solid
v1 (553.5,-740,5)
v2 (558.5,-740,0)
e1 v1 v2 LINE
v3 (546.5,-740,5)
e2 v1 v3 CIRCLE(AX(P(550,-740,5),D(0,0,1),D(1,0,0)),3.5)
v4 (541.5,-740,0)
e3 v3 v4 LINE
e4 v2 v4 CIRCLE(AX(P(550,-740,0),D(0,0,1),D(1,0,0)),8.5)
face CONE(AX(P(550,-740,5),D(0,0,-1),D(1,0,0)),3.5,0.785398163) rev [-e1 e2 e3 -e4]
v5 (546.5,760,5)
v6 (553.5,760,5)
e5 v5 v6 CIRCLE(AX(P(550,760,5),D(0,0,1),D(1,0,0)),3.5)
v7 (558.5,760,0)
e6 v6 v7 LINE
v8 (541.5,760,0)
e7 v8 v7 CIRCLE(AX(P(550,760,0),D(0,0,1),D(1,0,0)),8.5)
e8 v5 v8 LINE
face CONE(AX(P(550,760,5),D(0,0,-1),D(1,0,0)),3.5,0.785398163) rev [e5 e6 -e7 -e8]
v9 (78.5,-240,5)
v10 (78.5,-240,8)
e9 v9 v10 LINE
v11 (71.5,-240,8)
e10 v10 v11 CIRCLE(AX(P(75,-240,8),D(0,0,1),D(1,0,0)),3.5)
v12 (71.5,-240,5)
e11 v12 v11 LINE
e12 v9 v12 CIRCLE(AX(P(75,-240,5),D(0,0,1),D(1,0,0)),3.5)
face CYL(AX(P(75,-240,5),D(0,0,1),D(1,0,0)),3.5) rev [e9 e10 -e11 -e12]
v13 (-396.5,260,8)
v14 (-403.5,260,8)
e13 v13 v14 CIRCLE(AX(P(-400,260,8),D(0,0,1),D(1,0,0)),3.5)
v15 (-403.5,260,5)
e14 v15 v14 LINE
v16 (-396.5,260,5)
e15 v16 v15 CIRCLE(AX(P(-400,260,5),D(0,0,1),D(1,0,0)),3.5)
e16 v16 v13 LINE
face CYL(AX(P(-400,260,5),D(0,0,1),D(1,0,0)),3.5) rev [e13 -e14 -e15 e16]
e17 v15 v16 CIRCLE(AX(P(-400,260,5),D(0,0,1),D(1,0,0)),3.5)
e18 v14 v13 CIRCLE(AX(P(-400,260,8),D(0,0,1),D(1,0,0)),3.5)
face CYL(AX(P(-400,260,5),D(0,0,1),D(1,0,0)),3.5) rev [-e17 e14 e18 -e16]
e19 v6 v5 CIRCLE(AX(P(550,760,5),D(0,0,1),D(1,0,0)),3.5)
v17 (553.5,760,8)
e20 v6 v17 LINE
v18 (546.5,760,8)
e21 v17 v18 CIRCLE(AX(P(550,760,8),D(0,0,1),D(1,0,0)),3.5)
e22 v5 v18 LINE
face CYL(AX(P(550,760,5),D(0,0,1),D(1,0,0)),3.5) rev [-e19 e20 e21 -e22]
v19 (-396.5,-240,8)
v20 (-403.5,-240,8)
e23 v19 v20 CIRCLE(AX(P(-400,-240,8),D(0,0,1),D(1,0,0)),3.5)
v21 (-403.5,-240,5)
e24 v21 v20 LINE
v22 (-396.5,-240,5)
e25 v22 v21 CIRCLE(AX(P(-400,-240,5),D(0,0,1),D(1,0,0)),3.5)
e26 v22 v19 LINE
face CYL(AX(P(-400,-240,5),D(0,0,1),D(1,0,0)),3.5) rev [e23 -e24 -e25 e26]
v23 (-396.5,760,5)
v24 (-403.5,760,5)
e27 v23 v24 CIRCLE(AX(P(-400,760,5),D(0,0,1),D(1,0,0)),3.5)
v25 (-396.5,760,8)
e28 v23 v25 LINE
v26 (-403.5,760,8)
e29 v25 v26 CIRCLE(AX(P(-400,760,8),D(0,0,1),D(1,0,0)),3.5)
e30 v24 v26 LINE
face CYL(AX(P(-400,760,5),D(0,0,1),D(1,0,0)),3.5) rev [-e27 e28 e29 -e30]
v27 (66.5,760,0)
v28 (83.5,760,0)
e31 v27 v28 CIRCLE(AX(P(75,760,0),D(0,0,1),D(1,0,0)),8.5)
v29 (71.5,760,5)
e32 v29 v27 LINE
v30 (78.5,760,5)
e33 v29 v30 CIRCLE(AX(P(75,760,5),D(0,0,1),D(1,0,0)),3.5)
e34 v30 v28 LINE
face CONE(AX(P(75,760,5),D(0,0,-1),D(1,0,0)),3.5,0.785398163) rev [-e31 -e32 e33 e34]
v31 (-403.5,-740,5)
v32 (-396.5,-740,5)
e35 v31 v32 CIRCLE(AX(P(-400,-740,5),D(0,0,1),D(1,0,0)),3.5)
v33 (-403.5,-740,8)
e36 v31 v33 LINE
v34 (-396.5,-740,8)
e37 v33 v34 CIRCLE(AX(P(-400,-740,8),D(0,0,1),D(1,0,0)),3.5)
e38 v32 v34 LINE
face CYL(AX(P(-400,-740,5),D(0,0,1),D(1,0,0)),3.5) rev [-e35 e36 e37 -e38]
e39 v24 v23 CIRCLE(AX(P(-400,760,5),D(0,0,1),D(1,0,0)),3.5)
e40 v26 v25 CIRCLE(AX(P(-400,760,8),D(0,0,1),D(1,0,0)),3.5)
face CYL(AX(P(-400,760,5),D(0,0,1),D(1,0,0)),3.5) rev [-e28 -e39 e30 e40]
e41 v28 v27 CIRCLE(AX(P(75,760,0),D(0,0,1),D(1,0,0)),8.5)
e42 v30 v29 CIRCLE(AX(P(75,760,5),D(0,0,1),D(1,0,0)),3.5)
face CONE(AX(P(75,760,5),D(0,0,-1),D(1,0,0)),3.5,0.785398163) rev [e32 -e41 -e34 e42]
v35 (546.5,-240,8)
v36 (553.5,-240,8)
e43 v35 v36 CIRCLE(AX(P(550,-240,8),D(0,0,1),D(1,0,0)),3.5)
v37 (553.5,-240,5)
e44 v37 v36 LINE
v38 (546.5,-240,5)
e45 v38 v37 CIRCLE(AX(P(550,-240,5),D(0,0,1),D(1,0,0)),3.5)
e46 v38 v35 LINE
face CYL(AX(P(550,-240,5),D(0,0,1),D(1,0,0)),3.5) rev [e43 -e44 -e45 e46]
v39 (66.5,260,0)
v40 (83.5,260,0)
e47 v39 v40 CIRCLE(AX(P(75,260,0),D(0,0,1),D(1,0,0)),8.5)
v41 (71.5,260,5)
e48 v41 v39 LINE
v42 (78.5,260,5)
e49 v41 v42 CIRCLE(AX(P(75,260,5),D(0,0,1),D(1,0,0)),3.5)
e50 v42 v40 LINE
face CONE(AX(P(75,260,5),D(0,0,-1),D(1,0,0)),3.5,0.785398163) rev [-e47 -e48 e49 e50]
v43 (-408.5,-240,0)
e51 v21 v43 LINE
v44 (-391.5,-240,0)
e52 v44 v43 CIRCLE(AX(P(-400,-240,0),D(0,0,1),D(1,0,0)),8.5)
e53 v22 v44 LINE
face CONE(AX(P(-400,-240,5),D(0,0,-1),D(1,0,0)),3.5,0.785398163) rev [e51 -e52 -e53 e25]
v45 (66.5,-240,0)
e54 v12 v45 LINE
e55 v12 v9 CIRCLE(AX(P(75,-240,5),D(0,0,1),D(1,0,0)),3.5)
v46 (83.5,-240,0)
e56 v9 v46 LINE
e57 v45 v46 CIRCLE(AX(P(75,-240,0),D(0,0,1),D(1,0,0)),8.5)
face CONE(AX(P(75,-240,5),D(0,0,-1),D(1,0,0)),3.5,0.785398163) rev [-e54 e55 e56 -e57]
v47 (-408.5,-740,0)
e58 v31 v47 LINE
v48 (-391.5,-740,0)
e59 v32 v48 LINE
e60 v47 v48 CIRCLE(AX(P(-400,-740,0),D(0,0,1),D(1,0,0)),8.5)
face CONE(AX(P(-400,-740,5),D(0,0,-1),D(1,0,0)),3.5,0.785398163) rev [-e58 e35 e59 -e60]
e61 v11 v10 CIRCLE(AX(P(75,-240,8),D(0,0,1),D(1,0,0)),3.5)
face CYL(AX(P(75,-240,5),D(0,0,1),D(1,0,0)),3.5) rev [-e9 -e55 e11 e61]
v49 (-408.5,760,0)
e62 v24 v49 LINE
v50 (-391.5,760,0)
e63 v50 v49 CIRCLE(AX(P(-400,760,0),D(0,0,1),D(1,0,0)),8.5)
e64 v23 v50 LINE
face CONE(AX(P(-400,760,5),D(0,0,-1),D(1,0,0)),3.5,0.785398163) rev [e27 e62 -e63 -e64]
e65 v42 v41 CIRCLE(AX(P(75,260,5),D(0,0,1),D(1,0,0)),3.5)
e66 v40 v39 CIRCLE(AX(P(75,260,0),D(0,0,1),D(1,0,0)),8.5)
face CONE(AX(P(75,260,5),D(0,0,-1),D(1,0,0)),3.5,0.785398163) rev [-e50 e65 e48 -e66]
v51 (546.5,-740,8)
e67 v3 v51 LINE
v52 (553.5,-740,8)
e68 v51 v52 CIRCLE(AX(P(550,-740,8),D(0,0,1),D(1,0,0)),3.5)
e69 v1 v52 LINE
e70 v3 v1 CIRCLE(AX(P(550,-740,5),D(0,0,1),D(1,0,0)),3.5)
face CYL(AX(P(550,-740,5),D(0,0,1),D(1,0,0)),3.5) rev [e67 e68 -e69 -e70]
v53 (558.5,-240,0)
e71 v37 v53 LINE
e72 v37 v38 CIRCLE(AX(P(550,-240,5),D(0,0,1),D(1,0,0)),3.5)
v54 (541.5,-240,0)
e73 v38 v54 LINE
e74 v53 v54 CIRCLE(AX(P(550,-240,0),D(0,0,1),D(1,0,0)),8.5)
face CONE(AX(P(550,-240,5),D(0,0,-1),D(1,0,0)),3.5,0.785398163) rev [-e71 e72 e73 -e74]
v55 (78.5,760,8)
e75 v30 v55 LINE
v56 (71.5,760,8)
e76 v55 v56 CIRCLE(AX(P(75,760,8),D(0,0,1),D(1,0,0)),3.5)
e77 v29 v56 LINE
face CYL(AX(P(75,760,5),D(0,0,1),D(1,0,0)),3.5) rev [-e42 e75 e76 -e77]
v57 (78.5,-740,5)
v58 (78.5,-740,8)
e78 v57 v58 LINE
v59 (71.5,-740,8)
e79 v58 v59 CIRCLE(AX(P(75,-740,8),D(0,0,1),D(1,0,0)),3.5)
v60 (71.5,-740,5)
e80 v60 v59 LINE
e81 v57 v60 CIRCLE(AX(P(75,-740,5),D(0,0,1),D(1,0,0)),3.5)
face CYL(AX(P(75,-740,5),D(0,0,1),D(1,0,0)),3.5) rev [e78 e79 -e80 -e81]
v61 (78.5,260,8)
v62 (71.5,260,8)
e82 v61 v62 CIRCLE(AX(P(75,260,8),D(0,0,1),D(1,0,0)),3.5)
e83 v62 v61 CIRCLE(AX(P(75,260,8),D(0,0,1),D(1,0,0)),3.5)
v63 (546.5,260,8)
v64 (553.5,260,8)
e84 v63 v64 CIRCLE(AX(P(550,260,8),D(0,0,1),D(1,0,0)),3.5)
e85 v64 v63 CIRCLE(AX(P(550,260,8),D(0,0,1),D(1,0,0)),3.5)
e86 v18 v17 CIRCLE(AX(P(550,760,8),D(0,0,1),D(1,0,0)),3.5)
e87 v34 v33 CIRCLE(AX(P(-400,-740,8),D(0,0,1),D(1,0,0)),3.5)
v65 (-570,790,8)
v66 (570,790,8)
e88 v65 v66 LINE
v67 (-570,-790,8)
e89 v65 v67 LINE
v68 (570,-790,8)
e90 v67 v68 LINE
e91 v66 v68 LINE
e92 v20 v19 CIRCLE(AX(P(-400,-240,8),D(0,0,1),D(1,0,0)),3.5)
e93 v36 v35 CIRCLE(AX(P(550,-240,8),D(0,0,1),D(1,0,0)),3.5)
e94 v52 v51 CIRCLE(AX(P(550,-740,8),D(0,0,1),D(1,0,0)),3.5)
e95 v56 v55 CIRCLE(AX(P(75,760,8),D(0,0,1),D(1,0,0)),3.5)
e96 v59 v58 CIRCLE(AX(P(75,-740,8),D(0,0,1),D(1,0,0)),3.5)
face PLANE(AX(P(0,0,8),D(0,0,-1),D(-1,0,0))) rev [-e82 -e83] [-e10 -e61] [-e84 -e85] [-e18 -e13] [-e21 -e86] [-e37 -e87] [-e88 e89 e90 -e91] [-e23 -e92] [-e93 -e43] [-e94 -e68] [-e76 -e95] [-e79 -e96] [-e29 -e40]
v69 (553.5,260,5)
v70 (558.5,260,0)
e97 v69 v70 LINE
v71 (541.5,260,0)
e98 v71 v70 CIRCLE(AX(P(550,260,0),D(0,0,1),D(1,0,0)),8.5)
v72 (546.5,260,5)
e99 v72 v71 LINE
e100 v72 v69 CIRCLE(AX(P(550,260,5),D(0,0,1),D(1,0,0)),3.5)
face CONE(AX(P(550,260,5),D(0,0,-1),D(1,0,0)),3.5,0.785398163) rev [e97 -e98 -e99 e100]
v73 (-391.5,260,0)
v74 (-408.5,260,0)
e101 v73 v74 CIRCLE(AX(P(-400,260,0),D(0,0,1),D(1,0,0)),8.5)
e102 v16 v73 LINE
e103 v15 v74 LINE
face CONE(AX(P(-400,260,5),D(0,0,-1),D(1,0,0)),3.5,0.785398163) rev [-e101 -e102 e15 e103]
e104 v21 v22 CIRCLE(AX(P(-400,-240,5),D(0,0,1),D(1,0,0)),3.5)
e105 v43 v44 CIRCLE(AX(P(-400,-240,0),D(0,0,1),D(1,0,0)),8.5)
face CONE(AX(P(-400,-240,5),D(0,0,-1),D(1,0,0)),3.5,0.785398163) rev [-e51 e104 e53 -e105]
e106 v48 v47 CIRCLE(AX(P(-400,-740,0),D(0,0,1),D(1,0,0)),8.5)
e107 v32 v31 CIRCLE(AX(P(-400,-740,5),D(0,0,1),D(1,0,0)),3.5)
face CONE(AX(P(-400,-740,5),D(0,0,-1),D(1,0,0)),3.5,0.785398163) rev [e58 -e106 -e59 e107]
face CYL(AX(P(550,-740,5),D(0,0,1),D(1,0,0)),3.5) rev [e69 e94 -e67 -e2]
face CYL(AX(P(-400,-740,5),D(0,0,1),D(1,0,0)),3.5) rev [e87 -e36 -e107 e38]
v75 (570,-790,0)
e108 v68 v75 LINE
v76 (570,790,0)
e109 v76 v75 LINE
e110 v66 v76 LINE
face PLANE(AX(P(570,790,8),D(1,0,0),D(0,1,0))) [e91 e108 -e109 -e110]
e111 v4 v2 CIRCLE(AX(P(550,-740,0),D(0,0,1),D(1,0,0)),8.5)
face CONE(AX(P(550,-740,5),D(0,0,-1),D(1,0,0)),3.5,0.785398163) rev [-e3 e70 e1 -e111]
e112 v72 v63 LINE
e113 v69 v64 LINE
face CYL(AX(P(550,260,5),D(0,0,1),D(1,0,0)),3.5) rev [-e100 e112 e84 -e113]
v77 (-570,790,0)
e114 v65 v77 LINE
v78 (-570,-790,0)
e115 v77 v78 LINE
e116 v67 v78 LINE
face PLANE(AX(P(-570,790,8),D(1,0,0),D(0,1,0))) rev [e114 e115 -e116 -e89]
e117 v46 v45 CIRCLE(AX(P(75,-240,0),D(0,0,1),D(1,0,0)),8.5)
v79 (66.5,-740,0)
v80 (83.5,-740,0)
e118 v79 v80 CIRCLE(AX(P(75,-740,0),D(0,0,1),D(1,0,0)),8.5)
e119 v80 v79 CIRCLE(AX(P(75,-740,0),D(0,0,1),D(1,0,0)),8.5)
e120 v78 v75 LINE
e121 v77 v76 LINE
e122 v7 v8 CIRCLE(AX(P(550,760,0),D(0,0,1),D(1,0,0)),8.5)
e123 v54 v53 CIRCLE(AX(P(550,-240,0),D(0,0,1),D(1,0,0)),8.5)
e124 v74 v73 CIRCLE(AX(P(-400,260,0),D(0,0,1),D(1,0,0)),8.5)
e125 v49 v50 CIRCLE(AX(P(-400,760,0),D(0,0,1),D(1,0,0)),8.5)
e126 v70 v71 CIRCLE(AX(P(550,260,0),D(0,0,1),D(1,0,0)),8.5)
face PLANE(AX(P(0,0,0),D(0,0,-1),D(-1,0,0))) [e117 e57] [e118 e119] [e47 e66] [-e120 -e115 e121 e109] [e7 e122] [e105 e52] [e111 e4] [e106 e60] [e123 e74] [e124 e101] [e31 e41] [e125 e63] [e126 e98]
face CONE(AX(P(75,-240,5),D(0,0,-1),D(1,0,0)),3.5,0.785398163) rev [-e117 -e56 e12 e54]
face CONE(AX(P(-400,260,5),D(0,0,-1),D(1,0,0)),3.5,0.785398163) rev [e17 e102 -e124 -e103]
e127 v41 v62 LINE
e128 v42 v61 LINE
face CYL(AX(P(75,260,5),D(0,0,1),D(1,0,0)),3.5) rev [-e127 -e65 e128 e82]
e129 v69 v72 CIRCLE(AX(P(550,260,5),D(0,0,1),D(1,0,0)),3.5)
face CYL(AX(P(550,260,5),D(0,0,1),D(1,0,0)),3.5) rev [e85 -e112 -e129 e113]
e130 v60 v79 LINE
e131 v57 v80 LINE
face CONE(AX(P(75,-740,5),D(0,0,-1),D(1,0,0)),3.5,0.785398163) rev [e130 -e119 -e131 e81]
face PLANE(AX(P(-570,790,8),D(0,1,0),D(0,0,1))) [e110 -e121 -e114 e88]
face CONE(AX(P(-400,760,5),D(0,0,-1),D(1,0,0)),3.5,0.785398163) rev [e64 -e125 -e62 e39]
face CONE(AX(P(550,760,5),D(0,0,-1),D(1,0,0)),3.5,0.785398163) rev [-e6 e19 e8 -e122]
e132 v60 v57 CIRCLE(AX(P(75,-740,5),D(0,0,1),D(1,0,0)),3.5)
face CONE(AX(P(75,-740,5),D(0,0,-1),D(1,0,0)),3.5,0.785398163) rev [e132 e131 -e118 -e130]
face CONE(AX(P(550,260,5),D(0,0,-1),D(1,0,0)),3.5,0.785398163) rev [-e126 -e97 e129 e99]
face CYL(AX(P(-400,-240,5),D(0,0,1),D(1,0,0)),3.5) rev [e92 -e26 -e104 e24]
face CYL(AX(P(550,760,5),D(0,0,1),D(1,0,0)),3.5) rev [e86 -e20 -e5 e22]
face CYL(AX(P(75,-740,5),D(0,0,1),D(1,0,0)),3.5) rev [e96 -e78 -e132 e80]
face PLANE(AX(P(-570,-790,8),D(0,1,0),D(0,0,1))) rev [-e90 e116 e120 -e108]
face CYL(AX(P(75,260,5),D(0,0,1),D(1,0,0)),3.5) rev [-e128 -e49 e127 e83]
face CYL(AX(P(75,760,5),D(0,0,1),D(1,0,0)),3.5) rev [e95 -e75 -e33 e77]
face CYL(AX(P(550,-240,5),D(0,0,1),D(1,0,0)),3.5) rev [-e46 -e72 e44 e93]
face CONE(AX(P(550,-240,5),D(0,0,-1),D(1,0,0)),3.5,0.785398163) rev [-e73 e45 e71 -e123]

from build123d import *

# Parameters (mm, degrees)
SKETCH1_W                     = 1140
SKETCH1_H                     = 1580
BOSS_EXTRUDE1_DEPTH           = 8
SKETCH2_R                     = 3.5
CUT_EXTRUDE1_DEPTH            = 3
SKETCH3_R                     = 3.5
CUT_EXTRUDE2_DEPTH            = 5
CUT_EXTRUDE2_DRAFT            = 45
CUT_EXTRUDE2_PROFILE_2_DEPTH  = 5
CUT_EXTRUDE2_PROFILE_2_DRAFT  = 45
CUT_EXTRUDE2_PROFILE_3_DEPTH  = 5
CUT_EXTRUDE2_PROFILE_3_DRAFT  = 45
CUT_EXTRUDE2_PROFILE_4_DEPTH  = 5
CUT_EXTRUDE2_PROFILE_4_DRAFT  = 45
CUT_EXTRUDE2_PROFILE_5_DEPTH  = 5
CUT_EXTRUDE2_PROFILE_5_DRAFT  = 45
CUT_EXTRUDE2_PROFILE_6_DEPTH  = 5
CUT_EXTRUDE2_PROFILE_6_DRAFT  = 45
CUT_EXTRUDE2_PROFILE_7_DEPTH  = 5
CUT_EXTRUDE2_PROFILE_7_DRAFT  = 45
CUT_EXTRUDE2_PROFILE_8_DEPTH  = 5
CUT_EXTRUDE2_PROFILE_8_DRAFT  = 45
CUT_EXTRUDE2_PROFILE_9_DEPTH  = 5
CUT_EXTRUDE2_PROFILE_9_DRAFT  = 45
CUT_EXTRUDE2_PROFILE_10_DEPTH = 5
CUT_EXTRUDE2_PROFILE_10_DRAFT = 45
CUT_EXTRUDE2_PROFILE_11_DEPTH = 5
CUT_EXTRUDE2_PROFILE_11_DRAFT = 45
CUT_EXTRUDE2_PROFILE_12_DEPTH = 5
CUT_EXTRUDE2_PROFILE_12_DRAFT = 45


with BuildPart() as part:
    # Sketch1 → Boss-Extrude1 (new body)
    with BuildSketch(Plane.XY):
        Rectangle(SKETCH1_W, SKETCH1_H)
    extrude(amount=BOSS_EXTRUDE1_DEPTH)

    # Sketch2 → Cut-Extrude1 (cut)
    with BuildSketch(Plane.XY.offset(8)):
        with Locations((-400, -240)):
            Circle(SKETCH2_R)
        with Locations((75, -240)):
            Circle(SKETCH2_R)
        with Locations((550, -240)):
            Circle(SKETCH2_R)
        with Locations((-400, 260)):
            Circle(SKETCH2_R)
        with Locations((75, 260)):
            Circle(SKETCH2_R)
        with Locations((550, 260)):
            Circle(SKETCH2_R)
        with Locations((-400, 760)):
            Circle(SKETCH2_R)
        with Locations((75, 760)):
            Circle(SKETCH2_R)
        with Locations((550, 760)):
            Circle(SKETCH2_R)
        with Locations((-400, -740)):
            Circle(SKETCH2_R)
        with Locations((75, -740)):
            Circle(SKETCH2_R)
        with Locations((550, -740)):
            Circle(SKETCH2_R)
    extrude(amount=-CUT_EXTRUDE1_DEPTH, mode=Mode.SUBTRACT)


with BuildPart() as cut_extrude2_tool:
    # Sketch3 → Cut-Extrude2 (with draft: the straight prism first)
    with BuildSketch(Plane.XY.offset(5)):
        with Locations((550, -740)):
            Circle(SKETCH3_R)
    extrude(amount=-CUT_EXTRUDE2_DEPTH)
    # Cut-Extrude2: the draft: its side faces are tilted about the plane it starts from
    cut_extrude2_sides = [cut_extrude2_tool.faces().sort_by_distance(p)[0] for p in [
        (546.5, -740, 2.5),
    ]]
    draft(cut_extrude2_sides, Plane.XY.offset(5), CUT_EXTRUDE2_DRAFT)


with BuildPart() as part_1:
    add(part.part)

    # Cut-Extrude2: cut by cut_extrude2_tool
    add(cut_extrude2_tool.part, mode=Mode.SUBTRACT)


with BuildPart() as cut_extrude2_profile_2_tool:
    # Sketch3 → Cut-Extrude2 profile 2 (with draft: the straight prism first)
    with BuildSketch(Plane.XY.offset(5)):
        with Locations((75, -740)):
            Circle(SKETCH3_R)
    extrude(amount=-CUT_EXTRUDE2_PROFILE_2_DEPTH)
    # Cut-Extrude2 profile 2: the draft: its side faces are tilted about the plane it starts from
    cut_extrude2_profile_2_sides = [cut_extrude2_profile_2_tool.faces().sort_by_distance(p)[0] for p in [
        (71.5, -740, 2.5),
    ]]
    draft(cut_extrude2_profile_2_sides, Plane.XY.offset(5), CUT_EXTRUDE2_PROFILE_2_DRAFT)


with BuildPart() as part_2:
    add(part_1.part)

    # Cut-Extrude2 profile 2: cut by cut_extrude2_profile_2_tool
    add(cut_extrude2_profile_2_tool.part, mode=Mode.SUBTRACT)


with BuildPart() as cut_extrude2_profile_3_tool:
    # Sketch3 → Cut-Extrude2 profile 3 (with draft: the straight prism first)
    with BuildSketch(Plane.XY.offset(5)):
        with Locations((-400, -740)):
            Circle(SKETCH3_R)
    extrude(amount=-CUT_EXTRUDE2_PROFILE_3_DEPTH)
    # Cut-Extrude2 profile 3: the draft: its side faces are tilted about the plane it starts from
    cut_extrude2_profile_3_sides = [cut_extrude2_profile_3_tool.faces().sort_by_distance(p)[0] for p in [
        (-403.5, -740, 2.5),
    ]]
    draft(cut_extrude2_profile_3_sides, Plane.XY.offset(5), CUT_EXTRUDE2_PROFILE_3_DRAFT)


with BuildPart() as part_3:
    add(part_2.part)

    # Cut-Extrude2 profile 3: cut by cut_extrude2_profile_3_tool
    add(cut_extrude2_profile_3_tool.part, mode=Mode.SUBTRACT)


with BuildPart() as cut_extrude2_profile_4_tool:
    # Sketch3 → Cut-Extrude2 profile 4 (with draft: the straight prism first)
    with BuildSketch(Plane.XY.offset(5)):
        with Locations((-400, -240)):
            Circle(SKETCH3_R)
    extrude(amount=-CUT_EXTRUDE2_PROFILE_4_DEPTH)
    # Cut-Extrude2 profile 4: the draft: its side faces are tilted about the plane it starts from
    cut_extrude2_profile_4_sides = [cut_extrude2_profile_4_tool.faces().sort_by_distance(p)[0] for p in [
        (-403.5, -240, 2.5),
    ]]
    draft(cut_extrude2_profile_4_sides, Plane.XY.offset(5), CUT_EXTRUDE2_PROFILE_4_DRAFT)


with BuildPart() as part_4:
    add(part_3.part)

    # Cut-Extrude2 profile 4: cut by cut_extrude2_profile_4_tool
    add(cut_extrude2_profile_4_tool.part, mode=Mode.SUBTRACT)


with BuildPart() as cut_extrude2_profile_5_tool:
    # Sketch3 → Cut-Extrude2 profile 5 (with draft: the straight prism first)
    with BuildSketch(Plane.XY.offset(5)):
        with Locations((75, -240)):
            Circle(SKETCH3_R)
    extrude(amount=-CUT_EXTRUDE2_PROFILE_5_DEPTH)
    # Cut-Extrude2 profile 5: the draft: its side faces are tilted about the plane it starts from
    cut_extrude2_profile_5_sides = [cut_extrude2_profile_5_tool.faces().sort_by_distance(p)[0] for p in [
        (71.5, -240, 2.5),
    ]]
    draft(cut_extrude2_profile_5_sides, Plane.XY.offset(5), CUT_EXTRUDE2_PROFILE_5_DRAFT)


with BuildPart() as part_5:
    add(part_4.part)

    # Cut-Extrude2 profile 5: cut by cut_extrude2_profile_5_tool
    add(cut_extrude2_profile_5_tool.part, mode=Mode.SUBTRACT)


with BuildPart() as cut_extrude2_profile_6_tool:
    # Sketch3 → Cut-Extrude2 profile 6 (with draft: the straight prism first)
    with BuildSketch(Plane.XY.offset(5)):
        with Locations((550, -240)):
            Circle(SKETCH3_R)
    extrude(amount=-CUT_EXTRUDE2_PROFILE_6_DEPTH)
    # Cut-Extrude2 profile 6: the draft: its side faces are tilted about the plane it starts from
    cut_extrude2_profile_6_sides = [cut_extrude2_profile_6_tool.faces().sort_by_distance(p)[0] for p in [
        (546.5, -240, 2.5),
    ]]
    draft(cut_extrude2_profile_6_sides, Plane.XY.offset(5), CUT_EXTRUDE2_PROFILE_6_DRAFT)


with BuildPart() as part_6:
    add(part_5.part)

    # Cut-Extrude2 profile 6: cut by cut_extrude2_profile_6_tool
    add(cut_extrude2_profile_6_tool.part, mode=Mode.SUBTRACT)


with BuildPart() as cut_extrude2_profile_7_tool:
    # Sketch3 → Cut-Extrude2 profile 7 (with draft: the straight prism first)
    with BuildSketch(Plane.XY.offset(5)):
        with Locations((550, 260)):
            Circle(SKETCH3_R)
    extrude(amount=-CUT_EXTRUDE2_PROFILE_7_DEPTH)
    # Cut-Extrude2 profile 7: the draft: its side faces are tilted about the plane it starts from
    cut_extrude2_profile_7_sides = [cut_extrude2_profile_7_tool.faces().sort_by_distance(p)[0] for p in [
        (546.5, 260, 2.5),
    ]]
    draft(cut_extrude2_profile_7_sides, Plane.XY.offset(5), CUT_EXTRUDE2_PROFILE_7_DRAFT)


with BuildPart() as part_7:
    add(part_6.part)

    # Cut-Extrude2 profile 7: cut by cut_extrude2_profile_7_tool
    add(cut_extrude2_profile_7_tool.part, mode=Mode.SUBTRACT)


with BuildPart() as cut_extrude2_profile_8_tool:
    # Sketch3 → Cut-Extrude2 profile 8 (with draft: the straight prism first)
    with BuildSketch(Plane.XY.offset(5)):
        with Locations((75, 260)):
            Circle(SKETCH3_R)
    extrude(amount=-CUT_EXTRUDE2_PROFILE_8_DEPTH)
    # Cut-Extrude2 profile 8: the draft: its side faces are tilted about the plane it starts from
    cut_extrude2_profile_8_sides = [cut_extrude2_profile_8_tool.faces().sort_by_distance(p)[0] for p in [
        (71.5, 260, 2.5),
    ]]
    draft(cut_extrude2_profile_8_sides, Plane.XY.offset(5), CUT_EXTRUDE2_PROFILE_8_DRAFT)


with BuildPart() as part_8:
    add(part_7.part)

    # Cut-Extrude2 profile 8: cut by cut_extrude2_profile_8_tool
    add(cut_extrude2_profile_8_tool.part, mode=Mode.SUBTRACT)


with BuildPart() as cut_extrude2_profile_9_tool:
    # Sketch3 → Cut-Extrude2 profile 9 (with draft: the straight prism first)
    with BuildSketch(Plane.XY.offset(5)):
        with Locations((-400, 260)):
            Circle(SKETCH3_R)
    extrude(amount=-CUT_EXTRUDE2_PROFILE_9_DEPTH)
    # Cut-Extrude2 profile 9: the draft: its side faces are tilted about the plane it starts from
    cut_extrude2_profile_9_sides = [cut_extrude2_profile_9_tool.faces().sort_by_distance(p)[0] for p in [
        (-403.5, 260, 2.5),
    ]]
    draft(cut_extrude2_profile_9_sides, Plane.XY.offset(5), CUT_EXTRUDE2_PROFILE_9_DRAFT)


with BuildPart() as part_9:
    add(part_8.part)

    # Cut-Extrude2 profile 9: cut by cut_extrude2_profile_9_tool
    add(cut_extrude2_profile_9_tool.part, mode=Mode.SUBTRACT)


with BuildPart() as cut_extrude2_profile_10_tool:
    # Sketch3 → Cut-Extrude2 profile 10 (with draft: the straight prism first)
    with BuildSketch(Plane.XY.offset(5)):
        with Locations((550, 760)):
            Circle(SKETCH3_R)
    extrude(amount=-CUT_EXTRUDE2_PROFILE_10_DEPTH)
    # Cut-Extrude2 profile 10: the draft: its side faces are tilted about the plane it starts from
    cut_extrude2_profile_10_sides = [cut_extrude2_profile_10_tool.faces().sort_by_distance(p)[0] for p in [
        (546.5, 760, 2.5),
    ]]
    draft(cut_extrude2_profile_10_sides, Plane.XY.offset(5), CUT_EXTRUDE2_PROFILE_10_DRAFT)


with BuildPart() as part_10:
    add(part_9.part)

    # Cut-Extrude2 profile 10: cut by cut_extrude2_profile_10_tool
    add(cut_extrude2_profile_10_tool.part, mode=Mode.SUBTRACT)


with BuildPart() as cut_extrude2_profile_11_tool:
    # Sketch3 → Cut-Extrude2 profile 11 (with draft: the straight prism first)
    with BuildSketch(Plane.XY.offset(5)):
        with Locations((75, 760)):
            Circle(SKETCH3_R)
    extrude(amount=-CUT_EXTRUDE2_PROFILE_11_DEPTH)
    # Cut-Extrude2 profile 11: the draft: its side faces are tilted about the plane it starts from
    cut_extrude2_profile_11_sides = [cut_extrude2_profile_11_tool.faces().sort_by_distance(p)[0] for p in [
        (71.5, 760, 2.5),
    ]]
    draft(cut_extrude2_profile_11_sides, Plane.XY.offset(5), CUT_EXTRUDE2_PROFILE_11_DRAFT)


with BuildPart() as part_11:
    add(part_10.part)

    # Cut-Extrude2 profile 11: cut by cut_extrude2_profile_11_tool
    add(cut_extrude2_profile_11_tool.part, mode=Mode.SUBTRACT)


with BuildPart() as cut_extrude2_profile_12_tool:
    # Sketch3 → Cut-Extrude2 profile 12 (with draft: the straight prism first)
    with BuildSketch(Plane.XY.offset(5)):
        with Locations((-400, 760)):
            Circle(SKETCH3_R)
    extrude(amount=-CUT_EXTRUDE2_PROFILE_12_DEPTH)
    # Cut-Extrude2 profile 12: the draft: its side faces are tilted about the plane it starts from
    cut_extrude2_profile_12_sides = [cut_extrude2_profile_12_tool.faces().sort_by_distance(p)[0] for p in [
        (-403.5, 760, 2.5),
    ]]
    draft(cut_extrude2_profile_12_sides, Plane.XY.offset(5), CUT_EXTRUDE2_PROFILE_12_DRAFT)


with BuildPart() as part_12:
    add(part_11.part)

    # Cut-Extrude2 profile 12: cut by cut_extrude2_profile_12_tool
    add(cut_extrude2_profile_12_tool.part, mode=Mode.SUBTRACT)


solid = part_12.part
